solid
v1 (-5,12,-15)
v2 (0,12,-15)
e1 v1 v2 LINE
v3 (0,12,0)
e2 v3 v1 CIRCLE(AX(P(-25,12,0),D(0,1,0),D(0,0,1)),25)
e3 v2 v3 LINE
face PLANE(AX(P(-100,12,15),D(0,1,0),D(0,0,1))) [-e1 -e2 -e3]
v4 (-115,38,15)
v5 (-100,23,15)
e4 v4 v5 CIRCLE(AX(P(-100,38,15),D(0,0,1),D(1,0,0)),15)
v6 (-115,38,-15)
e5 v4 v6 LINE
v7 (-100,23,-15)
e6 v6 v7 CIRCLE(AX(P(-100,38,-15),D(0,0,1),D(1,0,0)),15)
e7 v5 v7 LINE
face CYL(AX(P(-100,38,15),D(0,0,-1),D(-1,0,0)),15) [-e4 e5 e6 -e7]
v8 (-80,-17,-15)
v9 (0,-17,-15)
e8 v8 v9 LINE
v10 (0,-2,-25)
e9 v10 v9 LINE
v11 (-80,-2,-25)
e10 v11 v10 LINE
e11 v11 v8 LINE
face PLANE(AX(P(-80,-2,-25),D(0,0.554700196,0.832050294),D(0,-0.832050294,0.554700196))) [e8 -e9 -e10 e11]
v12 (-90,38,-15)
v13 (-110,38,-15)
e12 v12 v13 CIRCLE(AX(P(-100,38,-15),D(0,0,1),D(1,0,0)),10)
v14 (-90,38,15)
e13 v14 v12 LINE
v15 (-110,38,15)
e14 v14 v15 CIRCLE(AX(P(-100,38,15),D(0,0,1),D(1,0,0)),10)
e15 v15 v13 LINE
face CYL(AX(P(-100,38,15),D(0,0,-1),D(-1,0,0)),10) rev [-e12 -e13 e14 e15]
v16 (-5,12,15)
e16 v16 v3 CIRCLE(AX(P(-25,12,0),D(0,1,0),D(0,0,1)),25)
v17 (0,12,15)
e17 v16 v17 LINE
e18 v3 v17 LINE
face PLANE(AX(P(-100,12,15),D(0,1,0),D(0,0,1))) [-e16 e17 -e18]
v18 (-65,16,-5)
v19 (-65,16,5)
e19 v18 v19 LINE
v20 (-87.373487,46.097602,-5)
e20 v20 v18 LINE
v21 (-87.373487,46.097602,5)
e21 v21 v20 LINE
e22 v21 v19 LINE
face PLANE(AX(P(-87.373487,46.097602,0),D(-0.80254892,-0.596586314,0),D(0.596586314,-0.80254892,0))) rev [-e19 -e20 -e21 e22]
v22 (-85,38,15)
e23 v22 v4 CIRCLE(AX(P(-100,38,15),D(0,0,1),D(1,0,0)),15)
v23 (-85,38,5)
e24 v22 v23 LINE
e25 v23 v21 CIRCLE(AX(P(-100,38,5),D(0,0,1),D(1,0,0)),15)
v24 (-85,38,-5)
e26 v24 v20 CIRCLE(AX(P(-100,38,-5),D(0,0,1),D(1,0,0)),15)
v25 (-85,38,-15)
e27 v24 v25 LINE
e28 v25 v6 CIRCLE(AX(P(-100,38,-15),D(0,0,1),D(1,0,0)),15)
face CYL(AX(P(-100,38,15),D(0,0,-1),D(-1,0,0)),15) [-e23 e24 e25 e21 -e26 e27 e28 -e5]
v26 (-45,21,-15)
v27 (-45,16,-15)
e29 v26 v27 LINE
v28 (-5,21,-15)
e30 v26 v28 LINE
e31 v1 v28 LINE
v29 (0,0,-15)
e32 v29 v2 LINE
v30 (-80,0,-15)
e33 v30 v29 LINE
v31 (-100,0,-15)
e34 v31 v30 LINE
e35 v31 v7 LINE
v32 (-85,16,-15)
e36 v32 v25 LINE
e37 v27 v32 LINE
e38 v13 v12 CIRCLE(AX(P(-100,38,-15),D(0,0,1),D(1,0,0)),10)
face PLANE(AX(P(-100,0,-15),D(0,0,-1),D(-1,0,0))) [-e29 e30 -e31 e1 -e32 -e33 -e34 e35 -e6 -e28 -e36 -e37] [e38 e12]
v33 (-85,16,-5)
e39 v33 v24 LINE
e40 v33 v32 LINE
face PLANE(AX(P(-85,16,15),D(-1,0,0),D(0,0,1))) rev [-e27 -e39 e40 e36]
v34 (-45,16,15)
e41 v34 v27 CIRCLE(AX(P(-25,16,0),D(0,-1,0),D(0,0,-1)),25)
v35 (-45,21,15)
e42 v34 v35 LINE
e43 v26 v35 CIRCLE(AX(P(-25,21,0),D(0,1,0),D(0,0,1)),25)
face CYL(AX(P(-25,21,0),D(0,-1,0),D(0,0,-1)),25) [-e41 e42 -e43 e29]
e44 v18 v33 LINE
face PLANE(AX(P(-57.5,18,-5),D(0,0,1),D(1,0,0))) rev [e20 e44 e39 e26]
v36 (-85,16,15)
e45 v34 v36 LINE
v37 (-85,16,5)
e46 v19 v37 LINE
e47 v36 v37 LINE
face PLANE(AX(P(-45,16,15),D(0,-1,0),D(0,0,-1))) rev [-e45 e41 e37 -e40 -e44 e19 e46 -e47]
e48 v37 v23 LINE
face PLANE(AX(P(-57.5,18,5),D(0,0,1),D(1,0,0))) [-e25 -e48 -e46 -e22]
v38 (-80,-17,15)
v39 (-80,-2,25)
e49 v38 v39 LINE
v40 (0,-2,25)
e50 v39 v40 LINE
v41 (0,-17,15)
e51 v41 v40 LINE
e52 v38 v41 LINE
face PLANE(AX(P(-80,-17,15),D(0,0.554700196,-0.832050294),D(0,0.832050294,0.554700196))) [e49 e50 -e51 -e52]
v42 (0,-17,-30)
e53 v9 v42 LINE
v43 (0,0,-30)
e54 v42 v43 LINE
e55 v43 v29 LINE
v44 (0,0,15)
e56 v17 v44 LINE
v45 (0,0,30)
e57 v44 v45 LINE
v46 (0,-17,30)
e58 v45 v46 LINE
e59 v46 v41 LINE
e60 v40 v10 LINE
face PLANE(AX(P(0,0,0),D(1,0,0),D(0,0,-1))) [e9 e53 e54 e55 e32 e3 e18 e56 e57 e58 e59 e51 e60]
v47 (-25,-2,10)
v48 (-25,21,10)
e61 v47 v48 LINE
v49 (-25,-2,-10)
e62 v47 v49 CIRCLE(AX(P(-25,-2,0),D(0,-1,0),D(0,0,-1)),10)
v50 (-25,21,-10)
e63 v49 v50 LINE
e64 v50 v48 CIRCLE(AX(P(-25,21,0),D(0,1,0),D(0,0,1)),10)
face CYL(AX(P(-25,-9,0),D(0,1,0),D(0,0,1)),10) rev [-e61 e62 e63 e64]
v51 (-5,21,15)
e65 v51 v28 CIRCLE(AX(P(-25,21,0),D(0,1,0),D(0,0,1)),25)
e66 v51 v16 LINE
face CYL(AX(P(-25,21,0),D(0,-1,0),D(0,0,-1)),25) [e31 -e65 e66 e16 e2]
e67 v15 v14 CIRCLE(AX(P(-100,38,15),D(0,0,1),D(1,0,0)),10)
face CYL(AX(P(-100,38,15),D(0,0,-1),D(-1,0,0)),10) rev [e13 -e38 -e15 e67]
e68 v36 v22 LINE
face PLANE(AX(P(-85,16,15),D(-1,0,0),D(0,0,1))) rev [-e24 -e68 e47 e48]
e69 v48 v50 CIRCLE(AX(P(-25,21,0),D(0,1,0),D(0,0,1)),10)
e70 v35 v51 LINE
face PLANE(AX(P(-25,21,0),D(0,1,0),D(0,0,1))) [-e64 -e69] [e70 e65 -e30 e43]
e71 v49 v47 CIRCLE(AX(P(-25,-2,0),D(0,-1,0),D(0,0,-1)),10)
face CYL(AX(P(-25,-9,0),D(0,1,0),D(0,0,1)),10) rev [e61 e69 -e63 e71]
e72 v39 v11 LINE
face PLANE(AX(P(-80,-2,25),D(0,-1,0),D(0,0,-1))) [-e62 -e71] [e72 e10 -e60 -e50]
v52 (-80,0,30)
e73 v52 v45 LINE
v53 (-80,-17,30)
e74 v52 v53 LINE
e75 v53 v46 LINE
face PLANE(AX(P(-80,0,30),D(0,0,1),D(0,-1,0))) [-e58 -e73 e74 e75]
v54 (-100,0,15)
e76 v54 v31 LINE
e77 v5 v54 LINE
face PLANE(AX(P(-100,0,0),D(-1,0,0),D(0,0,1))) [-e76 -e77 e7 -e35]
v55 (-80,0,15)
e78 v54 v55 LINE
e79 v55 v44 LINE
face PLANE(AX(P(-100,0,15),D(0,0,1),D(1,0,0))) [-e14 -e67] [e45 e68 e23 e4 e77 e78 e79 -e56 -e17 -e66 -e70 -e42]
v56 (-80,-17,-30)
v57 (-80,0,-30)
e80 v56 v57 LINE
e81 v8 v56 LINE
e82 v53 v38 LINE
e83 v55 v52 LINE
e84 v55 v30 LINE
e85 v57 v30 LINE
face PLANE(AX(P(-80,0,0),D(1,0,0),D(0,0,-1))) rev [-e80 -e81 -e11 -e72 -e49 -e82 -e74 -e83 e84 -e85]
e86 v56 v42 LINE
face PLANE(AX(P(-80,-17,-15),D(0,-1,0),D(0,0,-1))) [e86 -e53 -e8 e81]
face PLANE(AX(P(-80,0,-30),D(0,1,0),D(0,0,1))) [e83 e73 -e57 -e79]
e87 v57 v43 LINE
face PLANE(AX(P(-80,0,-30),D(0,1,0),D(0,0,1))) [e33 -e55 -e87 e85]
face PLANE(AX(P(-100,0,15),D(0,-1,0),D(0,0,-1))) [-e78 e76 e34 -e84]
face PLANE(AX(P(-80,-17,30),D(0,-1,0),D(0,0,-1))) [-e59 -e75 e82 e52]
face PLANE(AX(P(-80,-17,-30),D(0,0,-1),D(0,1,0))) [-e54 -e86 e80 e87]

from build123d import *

# Parameters (mm, degrees)
SLOTTED_BASE_BLOCK_DEPTH = 80
PIVOT_PAD_SKETCH_R       = 25
PIVOT_PAD_50_DEPTH       = 21
UPPER_BAR_SKETCH_W       = 30
UPPER_BAR_SKETCH_H       = 12
UPPER_BAR_DEPTH          = 100
THROUGH_SLOT_PROFILE_W   = 15
THROUGH_SLOT_PROFILE_H   = 21
THROUGH_SLOT_CUT_DEPTH   = 100
EYE_LUG_PROFILE_R        = 10
RAISED_EYE_LUG_DEPTH     = 15
LUG_SUPPORT_RIB_REACH    = 132.131
LUG_RIB_SKETCH_WALL_W    = 299.76392147
LUG_RIB_SKETCH_WALL_H    = 10
PAD_HOLE_SKETCH_R        = 10
PAD_HOLE_20_DEPTH        = 30


with BuildPart() as part:
    # Base Block Profile → Slotted Base Block (new body)
    with BuildSketch(Plane(origin=(0, 0, 0), x_dir=(0, 0, -1), z_dir=(1, 0, 0))):
        Polygon((30, 0), (-30, 0), (-30, -17), (-15, -17), (-25, -2), (25, -2), (15, -17), (30, -17), align=None)
    extrude(amount=-SLOTTED_BASE_BLOCK_DEPTH)

    # Pivot Pad Sketch → Pivot Pad Ø50 (add)
    with BuildSketch(Plane(origin=(0, 0, 0), x_dir=(1, 0, 0), z_dir=(0, 1, 0))):
        with Locations((-25, 0)):
            Circle(PIVOT_PAD_SKETCH_R)
    extrude(amount=PIVOT_PAD_50_DEPTH)

    # Upper Bar Sketch → Upper Bar (add)
    with BuildSketch(Plane(origin=(0, 0, 0), x_dir=(0, 0, -1), z_dir=(1, 0, 0))):
        with Locations((0, 6)):
            Rectangle(UPPER_BAR_SKETCH_W, UPPER_BAR_SKETCH_H)
    extrude(amount=-UPPER_BAR_DEPTH)

    # Through Slot Profile → Through Slot Cut (cut)
    with BuildSketch(Plane(origin=(0, 0, 0), x_dir=(0, 0, -1), z_dir=(1, 0, 0))):
        with Locations((-22.5, 10.5)):
            Rectangle(THROUGH_SLOT_PROFILE_W, THROUGH_SLOT_PROFILE_H)
        with Locations((22.5, 10.5)):
            Rectangle(THROUGH_SLOT_PROFILE_W, THROUGH_SLOT_PROFILE_H)
    extrude(amount=-THROUGH_SLOT_CUT_DEPTH, mode=Mode.SUBTRACT)

    # Eye Lug Profile → Raised Eye Lug (add, symmetric)
    with BuildSketch(Plane.XY):
        with BuildLine():
            Line((-85, 16), (-85, 38))
            ThreePointArc((-85, 38), (-110.606601718, 48.606601718), (-100, 23))
            Line((-100, 23), (-100, 12))
            Line((-100, 12), (-45, 12))
            Line((-45, 12), (-45, 16))
            Line((-45, 16), (-85, 16))
        make_face()
        with Locations((-100, 38)):
            Circle(EYE_LUG_PROFILE_R, mode=Mode.SUBTRACT)
    extrude(amount=RAISED_EYE_LUG_DEPTH, both=True)

    # Lug Rib Sketch wall → Lug Support Rib (add, up to next)
    with BuildSketch(Plane(origin=(-76.186743425, 31.048801232, 0), x_dir=(0.596586314149, -0.802548920484, 0), z_dir=(0.802548920484, 0.596586314149, 0)), mode=Mode.PRIVATE) as lug_support_rib_sk1:
        Rectangle(LUG_RIB_SKETCH_WALL_W, LUG_RIB_SKETCH_WALL_H)
    lug_support_rib_tool1 = extrude(lug_support_rib_sk1.sketch, amount=-LUG_SUPPORT_RIB_REACH, mode=Mode.PRIVATE) - part.part
    add(lug_support_rib_tool1.solids().sort_by_distance((-76.186743425, 31.048801232, 0))[0])

    # Pad Hole Sketch → Pad Hole Ø20 (cut)
    with BuildSketch(Plane(origin=(0, 21, 0), x_dir=(1, 0, 0), z_dir=(0, 1, 0))):
        with Locations(Location((-25, 0, 0), (0, 0, 270))):
            Circle(PAD_HOLE_SKETCH_R)
    extrude(amount=-PAD_HOLE_20_DEPTH, mode=Mode.SUBTRACT)


solid = part.part
